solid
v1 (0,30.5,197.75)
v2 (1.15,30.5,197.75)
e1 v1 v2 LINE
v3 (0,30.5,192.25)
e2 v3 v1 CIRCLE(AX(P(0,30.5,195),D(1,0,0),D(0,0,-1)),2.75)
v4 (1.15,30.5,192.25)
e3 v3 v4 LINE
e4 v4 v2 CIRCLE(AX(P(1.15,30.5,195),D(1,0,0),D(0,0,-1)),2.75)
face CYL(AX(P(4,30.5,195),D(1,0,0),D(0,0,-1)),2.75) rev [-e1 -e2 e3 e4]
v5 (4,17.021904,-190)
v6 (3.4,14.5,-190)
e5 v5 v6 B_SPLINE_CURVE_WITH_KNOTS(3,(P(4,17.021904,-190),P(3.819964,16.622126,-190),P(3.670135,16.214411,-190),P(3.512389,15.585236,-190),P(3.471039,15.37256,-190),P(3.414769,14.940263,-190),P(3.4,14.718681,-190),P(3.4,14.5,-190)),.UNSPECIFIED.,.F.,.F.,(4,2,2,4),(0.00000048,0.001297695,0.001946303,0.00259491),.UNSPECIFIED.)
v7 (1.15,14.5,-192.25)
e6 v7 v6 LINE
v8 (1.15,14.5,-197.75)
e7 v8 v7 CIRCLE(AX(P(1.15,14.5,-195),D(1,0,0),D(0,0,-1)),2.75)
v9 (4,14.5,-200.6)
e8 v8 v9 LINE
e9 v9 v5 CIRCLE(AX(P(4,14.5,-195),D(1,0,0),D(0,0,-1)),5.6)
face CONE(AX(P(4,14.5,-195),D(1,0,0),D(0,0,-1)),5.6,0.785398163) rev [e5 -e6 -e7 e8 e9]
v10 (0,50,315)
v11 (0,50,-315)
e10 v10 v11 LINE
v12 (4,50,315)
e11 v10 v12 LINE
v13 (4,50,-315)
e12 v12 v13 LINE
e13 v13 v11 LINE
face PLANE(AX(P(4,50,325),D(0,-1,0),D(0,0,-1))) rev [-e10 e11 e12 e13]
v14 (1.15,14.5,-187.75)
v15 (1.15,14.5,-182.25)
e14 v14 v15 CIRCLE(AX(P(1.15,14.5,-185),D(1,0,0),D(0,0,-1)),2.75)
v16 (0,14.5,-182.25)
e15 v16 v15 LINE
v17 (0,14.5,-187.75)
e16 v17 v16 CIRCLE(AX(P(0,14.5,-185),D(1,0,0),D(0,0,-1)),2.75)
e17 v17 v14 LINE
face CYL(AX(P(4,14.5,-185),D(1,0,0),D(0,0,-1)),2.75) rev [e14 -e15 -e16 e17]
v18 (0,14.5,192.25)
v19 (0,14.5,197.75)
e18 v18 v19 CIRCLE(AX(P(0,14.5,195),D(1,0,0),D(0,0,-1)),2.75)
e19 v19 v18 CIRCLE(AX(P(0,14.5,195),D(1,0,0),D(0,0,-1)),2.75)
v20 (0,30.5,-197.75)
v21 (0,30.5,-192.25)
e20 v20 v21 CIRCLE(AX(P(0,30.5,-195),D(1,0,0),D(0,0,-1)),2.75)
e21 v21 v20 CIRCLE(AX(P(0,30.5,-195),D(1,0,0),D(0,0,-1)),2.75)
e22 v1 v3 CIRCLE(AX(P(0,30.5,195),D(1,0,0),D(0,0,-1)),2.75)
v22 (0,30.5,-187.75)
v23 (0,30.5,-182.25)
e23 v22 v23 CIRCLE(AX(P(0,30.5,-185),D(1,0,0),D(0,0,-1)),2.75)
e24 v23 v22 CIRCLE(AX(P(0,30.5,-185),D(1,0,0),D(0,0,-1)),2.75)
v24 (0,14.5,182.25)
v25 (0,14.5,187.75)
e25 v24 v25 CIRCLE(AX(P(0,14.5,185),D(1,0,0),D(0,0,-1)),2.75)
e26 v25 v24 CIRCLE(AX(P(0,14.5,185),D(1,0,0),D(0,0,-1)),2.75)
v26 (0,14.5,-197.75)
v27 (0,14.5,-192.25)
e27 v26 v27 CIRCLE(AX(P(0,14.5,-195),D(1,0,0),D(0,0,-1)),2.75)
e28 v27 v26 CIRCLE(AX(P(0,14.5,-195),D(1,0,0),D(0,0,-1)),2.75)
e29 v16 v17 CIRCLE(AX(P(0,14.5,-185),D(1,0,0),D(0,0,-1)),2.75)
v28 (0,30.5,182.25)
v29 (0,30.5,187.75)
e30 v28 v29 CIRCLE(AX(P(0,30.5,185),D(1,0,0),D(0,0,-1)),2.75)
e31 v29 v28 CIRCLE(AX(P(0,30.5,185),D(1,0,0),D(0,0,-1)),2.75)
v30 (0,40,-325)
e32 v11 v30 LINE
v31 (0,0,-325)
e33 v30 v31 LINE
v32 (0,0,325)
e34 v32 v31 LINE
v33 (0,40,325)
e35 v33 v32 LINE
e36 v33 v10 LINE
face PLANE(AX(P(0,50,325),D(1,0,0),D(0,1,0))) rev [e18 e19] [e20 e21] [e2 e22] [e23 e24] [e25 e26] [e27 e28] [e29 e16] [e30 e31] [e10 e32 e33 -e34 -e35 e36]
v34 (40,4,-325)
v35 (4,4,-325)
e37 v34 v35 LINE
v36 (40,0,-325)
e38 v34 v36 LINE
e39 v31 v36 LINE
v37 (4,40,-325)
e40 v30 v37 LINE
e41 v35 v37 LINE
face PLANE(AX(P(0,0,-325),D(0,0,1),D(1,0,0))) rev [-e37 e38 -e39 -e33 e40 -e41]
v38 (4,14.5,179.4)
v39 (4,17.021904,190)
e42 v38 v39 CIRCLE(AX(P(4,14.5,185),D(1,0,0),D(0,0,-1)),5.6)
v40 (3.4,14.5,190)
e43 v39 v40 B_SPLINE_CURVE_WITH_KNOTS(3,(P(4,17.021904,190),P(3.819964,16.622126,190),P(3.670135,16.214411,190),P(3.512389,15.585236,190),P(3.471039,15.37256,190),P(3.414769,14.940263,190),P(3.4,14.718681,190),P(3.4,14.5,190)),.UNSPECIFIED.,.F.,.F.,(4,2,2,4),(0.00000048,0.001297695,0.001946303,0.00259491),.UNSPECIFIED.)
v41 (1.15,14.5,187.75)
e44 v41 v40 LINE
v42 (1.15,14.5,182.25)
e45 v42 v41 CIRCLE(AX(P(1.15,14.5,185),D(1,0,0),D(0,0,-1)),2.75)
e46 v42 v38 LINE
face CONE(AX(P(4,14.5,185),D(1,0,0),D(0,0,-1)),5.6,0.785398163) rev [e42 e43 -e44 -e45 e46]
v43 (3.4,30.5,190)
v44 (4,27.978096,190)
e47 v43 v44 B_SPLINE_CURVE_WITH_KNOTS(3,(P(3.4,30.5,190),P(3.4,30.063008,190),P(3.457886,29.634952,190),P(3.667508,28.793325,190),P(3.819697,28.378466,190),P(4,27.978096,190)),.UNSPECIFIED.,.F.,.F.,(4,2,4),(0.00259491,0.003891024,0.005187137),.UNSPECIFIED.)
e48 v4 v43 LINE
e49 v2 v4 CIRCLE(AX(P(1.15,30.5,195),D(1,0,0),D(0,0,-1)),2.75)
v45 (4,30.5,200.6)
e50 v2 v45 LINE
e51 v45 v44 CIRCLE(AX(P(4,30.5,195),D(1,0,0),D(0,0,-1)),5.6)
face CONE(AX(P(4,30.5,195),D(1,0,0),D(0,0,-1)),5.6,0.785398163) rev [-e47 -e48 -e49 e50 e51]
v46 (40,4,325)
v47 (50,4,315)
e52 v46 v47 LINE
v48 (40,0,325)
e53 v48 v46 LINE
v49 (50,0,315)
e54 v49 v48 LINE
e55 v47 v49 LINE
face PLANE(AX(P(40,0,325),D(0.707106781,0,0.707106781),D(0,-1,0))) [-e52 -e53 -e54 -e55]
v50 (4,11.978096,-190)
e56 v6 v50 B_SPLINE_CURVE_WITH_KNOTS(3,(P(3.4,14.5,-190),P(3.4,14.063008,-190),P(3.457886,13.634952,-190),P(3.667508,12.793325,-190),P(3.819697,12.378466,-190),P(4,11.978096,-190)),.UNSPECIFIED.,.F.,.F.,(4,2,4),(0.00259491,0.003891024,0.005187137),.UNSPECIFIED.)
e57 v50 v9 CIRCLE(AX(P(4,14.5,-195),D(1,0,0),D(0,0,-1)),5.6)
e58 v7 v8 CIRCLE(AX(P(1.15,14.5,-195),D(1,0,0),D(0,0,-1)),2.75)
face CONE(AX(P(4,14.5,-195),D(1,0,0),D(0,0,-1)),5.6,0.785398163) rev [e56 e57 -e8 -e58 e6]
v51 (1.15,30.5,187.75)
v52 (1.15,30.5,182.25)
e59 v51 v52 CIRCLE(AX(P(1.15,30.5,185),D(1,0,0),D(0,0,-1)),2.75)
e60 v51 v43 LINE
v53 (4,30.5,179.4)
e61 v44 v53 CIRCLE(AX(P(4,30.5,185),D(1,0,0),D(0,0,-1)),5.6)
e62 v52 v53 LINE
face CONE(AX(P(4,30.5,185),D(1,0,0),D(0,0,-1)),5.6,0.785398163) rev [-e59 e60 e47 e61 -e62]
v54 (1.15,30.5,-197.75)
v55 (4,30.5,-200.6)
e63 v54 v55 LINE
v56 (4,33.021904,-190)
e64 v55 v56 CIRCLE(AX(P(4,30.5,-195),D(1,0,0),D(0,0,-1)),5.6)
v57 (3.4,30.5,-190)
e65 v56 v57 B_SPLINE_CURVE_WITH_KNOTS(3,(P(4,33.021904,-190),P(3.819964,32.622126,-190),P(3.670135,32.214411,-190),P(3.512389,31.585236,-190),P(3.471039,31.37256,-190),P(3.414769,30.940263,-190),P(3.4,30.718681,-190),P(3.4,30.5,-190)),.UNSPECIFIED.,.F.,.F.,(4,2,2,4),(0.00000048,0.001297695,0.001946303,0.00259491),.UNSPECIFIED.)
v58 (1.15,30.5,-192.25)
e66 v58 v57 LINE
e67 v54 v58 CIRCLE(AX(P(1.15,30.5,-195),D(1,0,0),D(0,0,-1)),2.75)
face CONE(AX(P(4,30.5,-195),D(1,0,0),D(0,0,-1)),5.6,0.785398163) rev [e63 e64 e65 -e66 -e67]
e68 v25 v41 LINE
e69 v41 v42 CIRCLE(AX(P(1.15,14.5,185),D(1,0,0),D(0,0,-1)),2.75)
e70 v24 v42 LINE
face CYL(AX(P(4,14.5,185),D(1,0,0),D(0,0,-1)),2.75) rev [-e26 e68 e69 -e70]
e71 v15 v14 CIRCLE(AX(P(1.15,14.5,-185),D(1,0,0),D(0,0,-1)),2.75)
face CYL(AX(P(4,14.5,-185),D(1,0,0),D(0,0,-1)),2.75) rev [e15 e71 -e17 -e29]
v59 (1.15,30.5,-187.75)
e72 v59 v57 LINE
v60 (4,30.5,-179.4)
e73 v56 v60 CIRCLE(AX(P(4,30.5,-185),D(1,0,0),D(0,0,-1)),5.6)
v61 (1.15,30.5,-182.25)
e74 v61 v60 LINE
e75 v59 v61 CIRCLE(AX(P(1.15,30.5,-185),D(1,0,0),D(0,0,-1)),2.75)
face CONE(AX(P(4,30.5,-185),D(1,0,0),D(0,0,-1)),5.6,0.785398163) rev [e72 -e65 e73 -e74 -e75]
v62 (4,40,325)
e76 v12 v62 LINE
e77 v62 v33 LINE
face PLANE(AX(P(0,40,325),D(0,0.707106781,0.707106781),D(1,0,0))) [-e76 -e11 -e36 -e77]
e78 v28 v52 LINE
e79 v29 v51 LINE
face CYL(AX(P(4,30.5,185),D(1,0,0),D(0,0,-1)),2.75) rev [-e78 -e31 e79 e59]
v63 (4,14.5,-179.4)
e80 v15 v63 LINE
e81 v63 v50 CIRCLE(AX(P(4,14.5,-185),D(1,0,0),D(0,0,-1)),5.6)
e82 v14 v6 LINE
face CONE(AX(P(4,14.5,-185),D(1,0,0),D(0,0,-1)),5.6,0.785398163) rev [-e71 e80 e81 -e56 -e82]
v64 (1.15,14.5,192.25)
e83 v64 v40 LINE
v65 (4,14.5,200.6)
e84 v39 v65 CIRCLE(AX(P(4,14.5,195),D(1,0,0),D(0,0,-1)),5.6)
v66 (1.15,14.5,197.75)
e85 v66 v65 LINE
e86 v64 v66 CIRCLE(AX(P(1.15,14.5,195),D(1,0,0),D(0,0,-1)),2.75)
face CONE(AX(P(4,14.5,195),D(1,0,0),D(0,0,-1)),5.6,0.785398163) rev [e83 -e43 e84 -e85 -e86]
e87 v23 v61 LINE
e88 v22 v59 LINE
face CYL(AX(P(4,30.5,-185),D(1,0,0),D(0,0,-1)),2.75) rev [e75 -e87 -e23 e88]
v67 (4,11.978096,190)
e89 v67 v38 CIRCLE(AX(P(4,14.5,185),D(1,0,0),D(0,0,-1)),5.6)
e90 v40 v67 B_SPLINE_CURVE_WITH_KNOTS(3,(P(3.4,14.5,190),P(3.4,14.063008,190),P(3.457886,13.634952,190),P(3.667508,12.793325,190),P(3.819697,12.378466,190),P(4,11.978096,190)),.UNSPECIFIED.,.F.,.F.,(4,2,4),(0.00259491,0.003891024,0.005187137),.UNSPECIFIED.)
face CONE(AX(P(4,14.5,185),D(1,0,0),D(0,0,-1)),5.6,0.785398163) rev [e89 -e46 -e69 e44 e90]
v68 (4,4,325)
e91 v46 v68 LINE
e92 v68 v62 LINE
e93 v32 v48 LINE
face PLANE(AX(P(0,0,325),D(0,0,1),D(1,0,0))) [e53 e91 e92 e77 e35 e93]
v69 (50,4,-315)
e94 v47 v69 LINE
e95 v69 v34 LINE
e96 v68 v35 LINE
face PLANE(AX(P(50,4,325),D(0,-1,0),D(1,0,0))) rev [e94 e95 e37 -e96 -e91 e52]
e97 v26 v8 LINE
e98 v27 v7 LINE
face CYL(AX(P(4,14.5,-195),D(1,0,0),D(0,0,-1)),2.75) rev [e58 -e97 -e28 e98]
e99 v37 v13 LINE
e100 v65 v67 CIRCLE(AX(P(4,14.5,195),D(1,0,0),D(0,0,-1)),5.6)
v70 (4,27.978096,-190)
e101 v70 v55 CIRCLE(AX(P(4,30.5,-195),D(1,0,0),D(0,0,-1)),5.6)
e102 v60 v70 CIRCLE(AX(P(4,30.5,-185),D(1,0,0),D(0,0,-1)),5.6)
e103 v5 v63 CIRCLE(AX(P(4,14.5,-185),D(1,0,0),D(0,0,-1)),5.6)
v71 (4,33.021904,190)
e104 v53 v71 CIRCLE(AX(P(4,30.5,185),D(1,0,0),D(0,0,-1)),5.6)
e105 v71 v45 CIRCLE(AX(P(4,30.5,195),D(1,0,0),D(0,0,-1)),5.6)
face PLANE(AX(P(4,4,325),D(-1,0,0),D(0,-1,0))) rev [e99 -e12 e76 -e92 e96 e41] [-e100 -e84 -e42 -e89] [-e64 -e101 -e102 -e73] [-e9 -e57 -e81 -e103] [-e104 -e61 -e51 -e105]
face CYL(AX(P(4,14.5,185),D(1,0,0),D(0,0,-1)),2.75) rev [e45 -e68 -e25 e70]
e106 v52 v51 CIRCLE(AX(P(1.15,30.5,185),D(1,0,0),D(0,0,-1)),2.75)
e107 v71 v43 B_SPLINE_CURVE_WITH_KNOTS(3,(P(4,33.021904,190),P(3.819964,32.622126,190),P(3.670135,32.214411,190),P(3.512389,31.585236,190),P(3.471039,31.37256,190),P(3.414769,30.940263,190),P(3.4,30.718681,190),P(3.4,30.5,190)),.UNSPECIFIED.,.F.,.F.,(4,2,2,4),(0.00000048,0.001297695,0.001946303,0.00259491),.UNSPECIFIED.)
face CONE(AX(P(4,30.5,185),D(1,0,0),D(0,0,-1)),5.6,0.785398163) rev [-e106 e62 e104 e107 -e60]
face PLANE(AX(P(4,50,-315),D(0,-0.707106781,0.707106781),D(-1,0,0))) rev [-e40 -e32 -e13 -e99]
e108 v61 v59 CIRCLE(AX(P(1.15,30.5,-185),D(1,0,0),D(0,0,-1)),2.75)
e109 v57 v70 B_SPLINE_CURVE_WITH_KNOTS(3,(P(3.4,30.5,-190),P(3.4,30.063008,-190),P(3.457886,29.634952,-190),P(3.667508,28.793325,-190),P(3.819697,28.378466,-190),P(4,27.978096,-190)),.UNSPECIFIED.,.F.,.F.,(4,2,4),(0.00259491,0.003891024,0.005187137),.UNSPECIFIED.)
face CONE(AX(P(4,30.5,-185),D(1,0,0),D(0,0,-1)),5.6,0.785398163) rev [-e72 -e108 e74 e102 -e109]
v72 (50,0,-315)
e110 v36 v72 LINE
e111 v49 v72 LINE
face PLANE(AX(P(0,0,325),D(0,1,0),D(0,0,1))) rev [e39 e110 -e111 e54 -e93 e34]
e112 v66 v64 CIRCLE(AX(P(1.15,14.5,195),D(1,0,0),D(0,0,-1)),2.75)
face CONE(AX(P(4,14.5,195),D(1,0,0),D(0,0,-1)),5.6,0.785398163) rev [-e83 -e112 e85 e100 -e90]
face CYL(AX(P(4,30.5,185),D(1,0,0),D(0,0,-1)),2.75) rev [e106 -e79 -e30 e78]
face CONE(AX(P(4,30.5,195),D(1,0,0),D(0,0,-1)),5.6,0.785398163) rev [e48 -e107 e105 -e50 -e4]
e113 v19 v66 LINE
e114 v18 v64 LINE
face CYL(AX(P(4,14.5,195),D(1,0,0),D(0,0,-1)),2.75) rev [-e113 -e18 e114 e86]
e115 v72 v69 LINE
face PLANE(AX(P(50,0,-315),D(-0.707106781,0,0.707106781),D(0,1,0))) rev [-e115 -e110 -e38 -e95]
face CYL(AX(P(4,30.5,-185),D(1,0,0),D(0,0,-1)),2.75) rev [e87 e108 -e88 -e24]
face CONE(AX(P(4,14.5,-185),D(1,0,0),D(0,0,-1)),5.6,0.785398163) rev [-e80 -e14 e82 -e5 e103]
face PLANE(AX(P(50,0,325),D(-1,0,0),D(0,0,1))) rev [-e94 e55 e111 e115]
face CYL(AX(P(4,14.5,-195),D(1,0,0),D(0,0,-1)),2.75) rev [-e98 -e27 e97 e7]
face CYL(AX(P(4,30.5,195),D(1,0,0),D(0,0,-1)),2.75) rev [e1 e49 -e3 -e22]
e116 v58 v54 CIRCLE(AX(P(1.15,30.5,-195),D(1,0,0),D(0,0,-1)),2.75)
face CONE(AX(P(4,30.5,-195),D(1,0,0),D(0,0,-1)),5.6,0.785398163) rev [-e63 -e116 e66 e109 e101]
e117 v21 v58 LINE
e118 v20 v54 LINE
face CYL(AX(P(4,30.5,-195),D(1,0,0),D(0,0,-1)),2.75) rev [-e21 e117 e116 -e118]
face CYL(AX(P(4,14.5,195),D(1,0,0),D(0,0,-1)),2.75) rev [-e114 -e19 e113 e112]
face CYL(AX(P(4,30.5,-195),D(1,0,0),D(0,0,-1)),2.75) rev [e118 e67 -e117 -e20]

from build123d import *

# Parameters (mm, degrees)
EXTRUDE_1_DEPTH             = 325
CHAMFER_1_SIZE              = 10
HOLE_WIZARD_M5_2_AT_2_COUNT = 2
HOLE_WIZARD_M5_2_AT_2_PITCH = 380
HOLE_WIZARD_M5_2_AT_3_COUNT = 2
HOLE_WIZARD_M5_2_AT_3_PITCH = 10
HOLE_WIZARD_M5_2_AT_4_COUNT = 2
HOLE_WIZARD_M5_2_AT_4_PITCH = 390
HOLE_WIZARD_M5_2_AT_5_COUNT = 2
HOLE_WIZARD_M5_2_AT_5_PITCH = 16
HOLE_WIZARD_M5_2_AT_6_COUNT = 2
HOLE_WIZARD_M5_2_AT_6_PITCH = 380.336692945
HOLE_WIZARD_M5_2_AT_7_COUNT = 2
HOLE_WIZARD_M5_2_AT_7_PITCH = 18.867962264
HOLE_WIZARD_M5_2_AT_8_COUNT = 2
HOLE_WIZARD_M5_2_AT_8_PITCH = 390.328067144


with BuildPart() as part:
    # 草图1 → 凸台-拉伸1 (new, symmetric)
    with BuildSketch(Plane.XY):
        Polygon((0, 0), (50, 0), (50, 4), (4, 4), (4, 50), (0, 50), align=None)
    extrude(amount=EXTRUDE_1_DEPTH, both=True)

    # 倒角1
    chamfer_1_edges = [part.edges().sort_by_distance(p)[0] for p in [
        (50, 2, 325),
        (2, 50, 325),
        (2, 50, -325),
        (50, 2, -325),
    ]]
    chamfer(chamfer_1_edges, length=CHAMFER_1_SIZE)

    # 草图5 → M5 六角凹锥坑螺钉的锥形沉头孔2 (revolve, cut)
    with BuildSketch(Plane(origin=(4, 30.5, 195), x_dir=(0, 0, -1), z_dir=(0, 1, 0))):
        Polygon((0, 0), (0, 4), (2.75, 4), (2.75, 2.85), (5.6, 0), align=None)
    hole_wizard_m5_2 = revolve(axis=Axis((10.35, 30.5, 195), (-1, 0, 0)), mode=Mode.SUBTRACT)

    # M5 六角凹锥坑螺钉的锥形沉头孔2 at 2: M5 六角凹锥坑螺钉的锥形沉头孔2 ×2
    with Locations(*[(0, 0, -i * HOLE_WIZARD_M5_2_AT_2_PITCH) for i in range(1, HOLE_WIZARD_M5_2_AT_2_COUNT)]):
        add(hole_wizard_m5_2, mode=Mode.SUBTRACT)

    # M5 六角凹锥坑螺钉的锥形沉头孔2 at 3: M5 六角凹锥坑螺钉的锥形沉头孔2 ×2
    with Locations(*[(0, 0, -i * HOLE_WIZARD_M5_2_AT_3_PITCH) for i in range(1, HOLE_WIZARD_M5_2_AT_3_COUNT)]):
        add(hole_wizard_m5_2, mode=Mode.SUBTRACT)

    # M5 六角凹锥坑螺钉的锥形沉头孔2 at 4: M5 六角凹锥坑螺钉的锥形沉头孔2 ×2
    with Locations(*[(0, 0, -i * HOLE_WIZARD_M5_2_AT_4_PITCH) for i in range(1, HOLE_WIZARD_M5_2_AT_4_COUNT)]):
        add(hole_wizard_m5_2, mode=Mode.SUBTRACT)

    # M5 六角凹锥坑螺钉的锥形沉头孔2 at 5: M5 六角凹锥坑螺钉的锥形沉头孔2 ×2
    with Locations(*[(0, -i * HOLE_WIZARD_M5_2_AT_5_PITCH, 0) for i in range(1, HOLE_WIZARD_M5_2_AT_5_COUNT)]):
        add(hole_wizard_m5_2, mode=Mode.SUBTRACT)

    # M5 六角凹锥坑螺钉的锥形沉头孔2 at 6: M5 六角凹锥坑螺钉的锥形沉头孔2 ×2
    with Locations(*[Vector(0, -0.04206798948618002, -0.9991147502967769) * (i * HOLE_WIZARD_M5_2_AT_6_PITCH) for i in range(1, HOLE_WIZARD_M5_2_AT_6_COUNT)]):
        add(hole_wizard_m5_2, mode=Mode.SUBTRACT)

    # M5 六角凹锥坑螺钉的锥形沉头孔2 at 7: M5 六角凹锥坑螺钉的锥形沉头孔2 ×2
    with Locations(*[Vector(0, -0.8479983040050839, -0.5299989400031865) * (i * HOLE_WIZARD_M5_2_AT_7_PITCH) for i in range(1, HOLE_WIZARD_M5_2_AT_7_COUNT)]):
        add(hole_wizard_m5_2, mode=Mode.SUBTRACT)

    # M5 六角凹锥坑螺钉的锥形沉头孔2 at 8: M5 六角凹锥坑螺钉的锥形沉头孔2 ×2
    with Locations(*[Vector(0, -0.04099115935241401, -0.9991595092150928) * (i * HOLE_WIZARD_M5_2_AT_8_PITCH) for i in range(1, HOLE_WIZARD_M5_2_AT_8_COUNT)]):
        add(hole_wizard_m5_2, mode=Mode.SUBTRACT)


solid = part.part
